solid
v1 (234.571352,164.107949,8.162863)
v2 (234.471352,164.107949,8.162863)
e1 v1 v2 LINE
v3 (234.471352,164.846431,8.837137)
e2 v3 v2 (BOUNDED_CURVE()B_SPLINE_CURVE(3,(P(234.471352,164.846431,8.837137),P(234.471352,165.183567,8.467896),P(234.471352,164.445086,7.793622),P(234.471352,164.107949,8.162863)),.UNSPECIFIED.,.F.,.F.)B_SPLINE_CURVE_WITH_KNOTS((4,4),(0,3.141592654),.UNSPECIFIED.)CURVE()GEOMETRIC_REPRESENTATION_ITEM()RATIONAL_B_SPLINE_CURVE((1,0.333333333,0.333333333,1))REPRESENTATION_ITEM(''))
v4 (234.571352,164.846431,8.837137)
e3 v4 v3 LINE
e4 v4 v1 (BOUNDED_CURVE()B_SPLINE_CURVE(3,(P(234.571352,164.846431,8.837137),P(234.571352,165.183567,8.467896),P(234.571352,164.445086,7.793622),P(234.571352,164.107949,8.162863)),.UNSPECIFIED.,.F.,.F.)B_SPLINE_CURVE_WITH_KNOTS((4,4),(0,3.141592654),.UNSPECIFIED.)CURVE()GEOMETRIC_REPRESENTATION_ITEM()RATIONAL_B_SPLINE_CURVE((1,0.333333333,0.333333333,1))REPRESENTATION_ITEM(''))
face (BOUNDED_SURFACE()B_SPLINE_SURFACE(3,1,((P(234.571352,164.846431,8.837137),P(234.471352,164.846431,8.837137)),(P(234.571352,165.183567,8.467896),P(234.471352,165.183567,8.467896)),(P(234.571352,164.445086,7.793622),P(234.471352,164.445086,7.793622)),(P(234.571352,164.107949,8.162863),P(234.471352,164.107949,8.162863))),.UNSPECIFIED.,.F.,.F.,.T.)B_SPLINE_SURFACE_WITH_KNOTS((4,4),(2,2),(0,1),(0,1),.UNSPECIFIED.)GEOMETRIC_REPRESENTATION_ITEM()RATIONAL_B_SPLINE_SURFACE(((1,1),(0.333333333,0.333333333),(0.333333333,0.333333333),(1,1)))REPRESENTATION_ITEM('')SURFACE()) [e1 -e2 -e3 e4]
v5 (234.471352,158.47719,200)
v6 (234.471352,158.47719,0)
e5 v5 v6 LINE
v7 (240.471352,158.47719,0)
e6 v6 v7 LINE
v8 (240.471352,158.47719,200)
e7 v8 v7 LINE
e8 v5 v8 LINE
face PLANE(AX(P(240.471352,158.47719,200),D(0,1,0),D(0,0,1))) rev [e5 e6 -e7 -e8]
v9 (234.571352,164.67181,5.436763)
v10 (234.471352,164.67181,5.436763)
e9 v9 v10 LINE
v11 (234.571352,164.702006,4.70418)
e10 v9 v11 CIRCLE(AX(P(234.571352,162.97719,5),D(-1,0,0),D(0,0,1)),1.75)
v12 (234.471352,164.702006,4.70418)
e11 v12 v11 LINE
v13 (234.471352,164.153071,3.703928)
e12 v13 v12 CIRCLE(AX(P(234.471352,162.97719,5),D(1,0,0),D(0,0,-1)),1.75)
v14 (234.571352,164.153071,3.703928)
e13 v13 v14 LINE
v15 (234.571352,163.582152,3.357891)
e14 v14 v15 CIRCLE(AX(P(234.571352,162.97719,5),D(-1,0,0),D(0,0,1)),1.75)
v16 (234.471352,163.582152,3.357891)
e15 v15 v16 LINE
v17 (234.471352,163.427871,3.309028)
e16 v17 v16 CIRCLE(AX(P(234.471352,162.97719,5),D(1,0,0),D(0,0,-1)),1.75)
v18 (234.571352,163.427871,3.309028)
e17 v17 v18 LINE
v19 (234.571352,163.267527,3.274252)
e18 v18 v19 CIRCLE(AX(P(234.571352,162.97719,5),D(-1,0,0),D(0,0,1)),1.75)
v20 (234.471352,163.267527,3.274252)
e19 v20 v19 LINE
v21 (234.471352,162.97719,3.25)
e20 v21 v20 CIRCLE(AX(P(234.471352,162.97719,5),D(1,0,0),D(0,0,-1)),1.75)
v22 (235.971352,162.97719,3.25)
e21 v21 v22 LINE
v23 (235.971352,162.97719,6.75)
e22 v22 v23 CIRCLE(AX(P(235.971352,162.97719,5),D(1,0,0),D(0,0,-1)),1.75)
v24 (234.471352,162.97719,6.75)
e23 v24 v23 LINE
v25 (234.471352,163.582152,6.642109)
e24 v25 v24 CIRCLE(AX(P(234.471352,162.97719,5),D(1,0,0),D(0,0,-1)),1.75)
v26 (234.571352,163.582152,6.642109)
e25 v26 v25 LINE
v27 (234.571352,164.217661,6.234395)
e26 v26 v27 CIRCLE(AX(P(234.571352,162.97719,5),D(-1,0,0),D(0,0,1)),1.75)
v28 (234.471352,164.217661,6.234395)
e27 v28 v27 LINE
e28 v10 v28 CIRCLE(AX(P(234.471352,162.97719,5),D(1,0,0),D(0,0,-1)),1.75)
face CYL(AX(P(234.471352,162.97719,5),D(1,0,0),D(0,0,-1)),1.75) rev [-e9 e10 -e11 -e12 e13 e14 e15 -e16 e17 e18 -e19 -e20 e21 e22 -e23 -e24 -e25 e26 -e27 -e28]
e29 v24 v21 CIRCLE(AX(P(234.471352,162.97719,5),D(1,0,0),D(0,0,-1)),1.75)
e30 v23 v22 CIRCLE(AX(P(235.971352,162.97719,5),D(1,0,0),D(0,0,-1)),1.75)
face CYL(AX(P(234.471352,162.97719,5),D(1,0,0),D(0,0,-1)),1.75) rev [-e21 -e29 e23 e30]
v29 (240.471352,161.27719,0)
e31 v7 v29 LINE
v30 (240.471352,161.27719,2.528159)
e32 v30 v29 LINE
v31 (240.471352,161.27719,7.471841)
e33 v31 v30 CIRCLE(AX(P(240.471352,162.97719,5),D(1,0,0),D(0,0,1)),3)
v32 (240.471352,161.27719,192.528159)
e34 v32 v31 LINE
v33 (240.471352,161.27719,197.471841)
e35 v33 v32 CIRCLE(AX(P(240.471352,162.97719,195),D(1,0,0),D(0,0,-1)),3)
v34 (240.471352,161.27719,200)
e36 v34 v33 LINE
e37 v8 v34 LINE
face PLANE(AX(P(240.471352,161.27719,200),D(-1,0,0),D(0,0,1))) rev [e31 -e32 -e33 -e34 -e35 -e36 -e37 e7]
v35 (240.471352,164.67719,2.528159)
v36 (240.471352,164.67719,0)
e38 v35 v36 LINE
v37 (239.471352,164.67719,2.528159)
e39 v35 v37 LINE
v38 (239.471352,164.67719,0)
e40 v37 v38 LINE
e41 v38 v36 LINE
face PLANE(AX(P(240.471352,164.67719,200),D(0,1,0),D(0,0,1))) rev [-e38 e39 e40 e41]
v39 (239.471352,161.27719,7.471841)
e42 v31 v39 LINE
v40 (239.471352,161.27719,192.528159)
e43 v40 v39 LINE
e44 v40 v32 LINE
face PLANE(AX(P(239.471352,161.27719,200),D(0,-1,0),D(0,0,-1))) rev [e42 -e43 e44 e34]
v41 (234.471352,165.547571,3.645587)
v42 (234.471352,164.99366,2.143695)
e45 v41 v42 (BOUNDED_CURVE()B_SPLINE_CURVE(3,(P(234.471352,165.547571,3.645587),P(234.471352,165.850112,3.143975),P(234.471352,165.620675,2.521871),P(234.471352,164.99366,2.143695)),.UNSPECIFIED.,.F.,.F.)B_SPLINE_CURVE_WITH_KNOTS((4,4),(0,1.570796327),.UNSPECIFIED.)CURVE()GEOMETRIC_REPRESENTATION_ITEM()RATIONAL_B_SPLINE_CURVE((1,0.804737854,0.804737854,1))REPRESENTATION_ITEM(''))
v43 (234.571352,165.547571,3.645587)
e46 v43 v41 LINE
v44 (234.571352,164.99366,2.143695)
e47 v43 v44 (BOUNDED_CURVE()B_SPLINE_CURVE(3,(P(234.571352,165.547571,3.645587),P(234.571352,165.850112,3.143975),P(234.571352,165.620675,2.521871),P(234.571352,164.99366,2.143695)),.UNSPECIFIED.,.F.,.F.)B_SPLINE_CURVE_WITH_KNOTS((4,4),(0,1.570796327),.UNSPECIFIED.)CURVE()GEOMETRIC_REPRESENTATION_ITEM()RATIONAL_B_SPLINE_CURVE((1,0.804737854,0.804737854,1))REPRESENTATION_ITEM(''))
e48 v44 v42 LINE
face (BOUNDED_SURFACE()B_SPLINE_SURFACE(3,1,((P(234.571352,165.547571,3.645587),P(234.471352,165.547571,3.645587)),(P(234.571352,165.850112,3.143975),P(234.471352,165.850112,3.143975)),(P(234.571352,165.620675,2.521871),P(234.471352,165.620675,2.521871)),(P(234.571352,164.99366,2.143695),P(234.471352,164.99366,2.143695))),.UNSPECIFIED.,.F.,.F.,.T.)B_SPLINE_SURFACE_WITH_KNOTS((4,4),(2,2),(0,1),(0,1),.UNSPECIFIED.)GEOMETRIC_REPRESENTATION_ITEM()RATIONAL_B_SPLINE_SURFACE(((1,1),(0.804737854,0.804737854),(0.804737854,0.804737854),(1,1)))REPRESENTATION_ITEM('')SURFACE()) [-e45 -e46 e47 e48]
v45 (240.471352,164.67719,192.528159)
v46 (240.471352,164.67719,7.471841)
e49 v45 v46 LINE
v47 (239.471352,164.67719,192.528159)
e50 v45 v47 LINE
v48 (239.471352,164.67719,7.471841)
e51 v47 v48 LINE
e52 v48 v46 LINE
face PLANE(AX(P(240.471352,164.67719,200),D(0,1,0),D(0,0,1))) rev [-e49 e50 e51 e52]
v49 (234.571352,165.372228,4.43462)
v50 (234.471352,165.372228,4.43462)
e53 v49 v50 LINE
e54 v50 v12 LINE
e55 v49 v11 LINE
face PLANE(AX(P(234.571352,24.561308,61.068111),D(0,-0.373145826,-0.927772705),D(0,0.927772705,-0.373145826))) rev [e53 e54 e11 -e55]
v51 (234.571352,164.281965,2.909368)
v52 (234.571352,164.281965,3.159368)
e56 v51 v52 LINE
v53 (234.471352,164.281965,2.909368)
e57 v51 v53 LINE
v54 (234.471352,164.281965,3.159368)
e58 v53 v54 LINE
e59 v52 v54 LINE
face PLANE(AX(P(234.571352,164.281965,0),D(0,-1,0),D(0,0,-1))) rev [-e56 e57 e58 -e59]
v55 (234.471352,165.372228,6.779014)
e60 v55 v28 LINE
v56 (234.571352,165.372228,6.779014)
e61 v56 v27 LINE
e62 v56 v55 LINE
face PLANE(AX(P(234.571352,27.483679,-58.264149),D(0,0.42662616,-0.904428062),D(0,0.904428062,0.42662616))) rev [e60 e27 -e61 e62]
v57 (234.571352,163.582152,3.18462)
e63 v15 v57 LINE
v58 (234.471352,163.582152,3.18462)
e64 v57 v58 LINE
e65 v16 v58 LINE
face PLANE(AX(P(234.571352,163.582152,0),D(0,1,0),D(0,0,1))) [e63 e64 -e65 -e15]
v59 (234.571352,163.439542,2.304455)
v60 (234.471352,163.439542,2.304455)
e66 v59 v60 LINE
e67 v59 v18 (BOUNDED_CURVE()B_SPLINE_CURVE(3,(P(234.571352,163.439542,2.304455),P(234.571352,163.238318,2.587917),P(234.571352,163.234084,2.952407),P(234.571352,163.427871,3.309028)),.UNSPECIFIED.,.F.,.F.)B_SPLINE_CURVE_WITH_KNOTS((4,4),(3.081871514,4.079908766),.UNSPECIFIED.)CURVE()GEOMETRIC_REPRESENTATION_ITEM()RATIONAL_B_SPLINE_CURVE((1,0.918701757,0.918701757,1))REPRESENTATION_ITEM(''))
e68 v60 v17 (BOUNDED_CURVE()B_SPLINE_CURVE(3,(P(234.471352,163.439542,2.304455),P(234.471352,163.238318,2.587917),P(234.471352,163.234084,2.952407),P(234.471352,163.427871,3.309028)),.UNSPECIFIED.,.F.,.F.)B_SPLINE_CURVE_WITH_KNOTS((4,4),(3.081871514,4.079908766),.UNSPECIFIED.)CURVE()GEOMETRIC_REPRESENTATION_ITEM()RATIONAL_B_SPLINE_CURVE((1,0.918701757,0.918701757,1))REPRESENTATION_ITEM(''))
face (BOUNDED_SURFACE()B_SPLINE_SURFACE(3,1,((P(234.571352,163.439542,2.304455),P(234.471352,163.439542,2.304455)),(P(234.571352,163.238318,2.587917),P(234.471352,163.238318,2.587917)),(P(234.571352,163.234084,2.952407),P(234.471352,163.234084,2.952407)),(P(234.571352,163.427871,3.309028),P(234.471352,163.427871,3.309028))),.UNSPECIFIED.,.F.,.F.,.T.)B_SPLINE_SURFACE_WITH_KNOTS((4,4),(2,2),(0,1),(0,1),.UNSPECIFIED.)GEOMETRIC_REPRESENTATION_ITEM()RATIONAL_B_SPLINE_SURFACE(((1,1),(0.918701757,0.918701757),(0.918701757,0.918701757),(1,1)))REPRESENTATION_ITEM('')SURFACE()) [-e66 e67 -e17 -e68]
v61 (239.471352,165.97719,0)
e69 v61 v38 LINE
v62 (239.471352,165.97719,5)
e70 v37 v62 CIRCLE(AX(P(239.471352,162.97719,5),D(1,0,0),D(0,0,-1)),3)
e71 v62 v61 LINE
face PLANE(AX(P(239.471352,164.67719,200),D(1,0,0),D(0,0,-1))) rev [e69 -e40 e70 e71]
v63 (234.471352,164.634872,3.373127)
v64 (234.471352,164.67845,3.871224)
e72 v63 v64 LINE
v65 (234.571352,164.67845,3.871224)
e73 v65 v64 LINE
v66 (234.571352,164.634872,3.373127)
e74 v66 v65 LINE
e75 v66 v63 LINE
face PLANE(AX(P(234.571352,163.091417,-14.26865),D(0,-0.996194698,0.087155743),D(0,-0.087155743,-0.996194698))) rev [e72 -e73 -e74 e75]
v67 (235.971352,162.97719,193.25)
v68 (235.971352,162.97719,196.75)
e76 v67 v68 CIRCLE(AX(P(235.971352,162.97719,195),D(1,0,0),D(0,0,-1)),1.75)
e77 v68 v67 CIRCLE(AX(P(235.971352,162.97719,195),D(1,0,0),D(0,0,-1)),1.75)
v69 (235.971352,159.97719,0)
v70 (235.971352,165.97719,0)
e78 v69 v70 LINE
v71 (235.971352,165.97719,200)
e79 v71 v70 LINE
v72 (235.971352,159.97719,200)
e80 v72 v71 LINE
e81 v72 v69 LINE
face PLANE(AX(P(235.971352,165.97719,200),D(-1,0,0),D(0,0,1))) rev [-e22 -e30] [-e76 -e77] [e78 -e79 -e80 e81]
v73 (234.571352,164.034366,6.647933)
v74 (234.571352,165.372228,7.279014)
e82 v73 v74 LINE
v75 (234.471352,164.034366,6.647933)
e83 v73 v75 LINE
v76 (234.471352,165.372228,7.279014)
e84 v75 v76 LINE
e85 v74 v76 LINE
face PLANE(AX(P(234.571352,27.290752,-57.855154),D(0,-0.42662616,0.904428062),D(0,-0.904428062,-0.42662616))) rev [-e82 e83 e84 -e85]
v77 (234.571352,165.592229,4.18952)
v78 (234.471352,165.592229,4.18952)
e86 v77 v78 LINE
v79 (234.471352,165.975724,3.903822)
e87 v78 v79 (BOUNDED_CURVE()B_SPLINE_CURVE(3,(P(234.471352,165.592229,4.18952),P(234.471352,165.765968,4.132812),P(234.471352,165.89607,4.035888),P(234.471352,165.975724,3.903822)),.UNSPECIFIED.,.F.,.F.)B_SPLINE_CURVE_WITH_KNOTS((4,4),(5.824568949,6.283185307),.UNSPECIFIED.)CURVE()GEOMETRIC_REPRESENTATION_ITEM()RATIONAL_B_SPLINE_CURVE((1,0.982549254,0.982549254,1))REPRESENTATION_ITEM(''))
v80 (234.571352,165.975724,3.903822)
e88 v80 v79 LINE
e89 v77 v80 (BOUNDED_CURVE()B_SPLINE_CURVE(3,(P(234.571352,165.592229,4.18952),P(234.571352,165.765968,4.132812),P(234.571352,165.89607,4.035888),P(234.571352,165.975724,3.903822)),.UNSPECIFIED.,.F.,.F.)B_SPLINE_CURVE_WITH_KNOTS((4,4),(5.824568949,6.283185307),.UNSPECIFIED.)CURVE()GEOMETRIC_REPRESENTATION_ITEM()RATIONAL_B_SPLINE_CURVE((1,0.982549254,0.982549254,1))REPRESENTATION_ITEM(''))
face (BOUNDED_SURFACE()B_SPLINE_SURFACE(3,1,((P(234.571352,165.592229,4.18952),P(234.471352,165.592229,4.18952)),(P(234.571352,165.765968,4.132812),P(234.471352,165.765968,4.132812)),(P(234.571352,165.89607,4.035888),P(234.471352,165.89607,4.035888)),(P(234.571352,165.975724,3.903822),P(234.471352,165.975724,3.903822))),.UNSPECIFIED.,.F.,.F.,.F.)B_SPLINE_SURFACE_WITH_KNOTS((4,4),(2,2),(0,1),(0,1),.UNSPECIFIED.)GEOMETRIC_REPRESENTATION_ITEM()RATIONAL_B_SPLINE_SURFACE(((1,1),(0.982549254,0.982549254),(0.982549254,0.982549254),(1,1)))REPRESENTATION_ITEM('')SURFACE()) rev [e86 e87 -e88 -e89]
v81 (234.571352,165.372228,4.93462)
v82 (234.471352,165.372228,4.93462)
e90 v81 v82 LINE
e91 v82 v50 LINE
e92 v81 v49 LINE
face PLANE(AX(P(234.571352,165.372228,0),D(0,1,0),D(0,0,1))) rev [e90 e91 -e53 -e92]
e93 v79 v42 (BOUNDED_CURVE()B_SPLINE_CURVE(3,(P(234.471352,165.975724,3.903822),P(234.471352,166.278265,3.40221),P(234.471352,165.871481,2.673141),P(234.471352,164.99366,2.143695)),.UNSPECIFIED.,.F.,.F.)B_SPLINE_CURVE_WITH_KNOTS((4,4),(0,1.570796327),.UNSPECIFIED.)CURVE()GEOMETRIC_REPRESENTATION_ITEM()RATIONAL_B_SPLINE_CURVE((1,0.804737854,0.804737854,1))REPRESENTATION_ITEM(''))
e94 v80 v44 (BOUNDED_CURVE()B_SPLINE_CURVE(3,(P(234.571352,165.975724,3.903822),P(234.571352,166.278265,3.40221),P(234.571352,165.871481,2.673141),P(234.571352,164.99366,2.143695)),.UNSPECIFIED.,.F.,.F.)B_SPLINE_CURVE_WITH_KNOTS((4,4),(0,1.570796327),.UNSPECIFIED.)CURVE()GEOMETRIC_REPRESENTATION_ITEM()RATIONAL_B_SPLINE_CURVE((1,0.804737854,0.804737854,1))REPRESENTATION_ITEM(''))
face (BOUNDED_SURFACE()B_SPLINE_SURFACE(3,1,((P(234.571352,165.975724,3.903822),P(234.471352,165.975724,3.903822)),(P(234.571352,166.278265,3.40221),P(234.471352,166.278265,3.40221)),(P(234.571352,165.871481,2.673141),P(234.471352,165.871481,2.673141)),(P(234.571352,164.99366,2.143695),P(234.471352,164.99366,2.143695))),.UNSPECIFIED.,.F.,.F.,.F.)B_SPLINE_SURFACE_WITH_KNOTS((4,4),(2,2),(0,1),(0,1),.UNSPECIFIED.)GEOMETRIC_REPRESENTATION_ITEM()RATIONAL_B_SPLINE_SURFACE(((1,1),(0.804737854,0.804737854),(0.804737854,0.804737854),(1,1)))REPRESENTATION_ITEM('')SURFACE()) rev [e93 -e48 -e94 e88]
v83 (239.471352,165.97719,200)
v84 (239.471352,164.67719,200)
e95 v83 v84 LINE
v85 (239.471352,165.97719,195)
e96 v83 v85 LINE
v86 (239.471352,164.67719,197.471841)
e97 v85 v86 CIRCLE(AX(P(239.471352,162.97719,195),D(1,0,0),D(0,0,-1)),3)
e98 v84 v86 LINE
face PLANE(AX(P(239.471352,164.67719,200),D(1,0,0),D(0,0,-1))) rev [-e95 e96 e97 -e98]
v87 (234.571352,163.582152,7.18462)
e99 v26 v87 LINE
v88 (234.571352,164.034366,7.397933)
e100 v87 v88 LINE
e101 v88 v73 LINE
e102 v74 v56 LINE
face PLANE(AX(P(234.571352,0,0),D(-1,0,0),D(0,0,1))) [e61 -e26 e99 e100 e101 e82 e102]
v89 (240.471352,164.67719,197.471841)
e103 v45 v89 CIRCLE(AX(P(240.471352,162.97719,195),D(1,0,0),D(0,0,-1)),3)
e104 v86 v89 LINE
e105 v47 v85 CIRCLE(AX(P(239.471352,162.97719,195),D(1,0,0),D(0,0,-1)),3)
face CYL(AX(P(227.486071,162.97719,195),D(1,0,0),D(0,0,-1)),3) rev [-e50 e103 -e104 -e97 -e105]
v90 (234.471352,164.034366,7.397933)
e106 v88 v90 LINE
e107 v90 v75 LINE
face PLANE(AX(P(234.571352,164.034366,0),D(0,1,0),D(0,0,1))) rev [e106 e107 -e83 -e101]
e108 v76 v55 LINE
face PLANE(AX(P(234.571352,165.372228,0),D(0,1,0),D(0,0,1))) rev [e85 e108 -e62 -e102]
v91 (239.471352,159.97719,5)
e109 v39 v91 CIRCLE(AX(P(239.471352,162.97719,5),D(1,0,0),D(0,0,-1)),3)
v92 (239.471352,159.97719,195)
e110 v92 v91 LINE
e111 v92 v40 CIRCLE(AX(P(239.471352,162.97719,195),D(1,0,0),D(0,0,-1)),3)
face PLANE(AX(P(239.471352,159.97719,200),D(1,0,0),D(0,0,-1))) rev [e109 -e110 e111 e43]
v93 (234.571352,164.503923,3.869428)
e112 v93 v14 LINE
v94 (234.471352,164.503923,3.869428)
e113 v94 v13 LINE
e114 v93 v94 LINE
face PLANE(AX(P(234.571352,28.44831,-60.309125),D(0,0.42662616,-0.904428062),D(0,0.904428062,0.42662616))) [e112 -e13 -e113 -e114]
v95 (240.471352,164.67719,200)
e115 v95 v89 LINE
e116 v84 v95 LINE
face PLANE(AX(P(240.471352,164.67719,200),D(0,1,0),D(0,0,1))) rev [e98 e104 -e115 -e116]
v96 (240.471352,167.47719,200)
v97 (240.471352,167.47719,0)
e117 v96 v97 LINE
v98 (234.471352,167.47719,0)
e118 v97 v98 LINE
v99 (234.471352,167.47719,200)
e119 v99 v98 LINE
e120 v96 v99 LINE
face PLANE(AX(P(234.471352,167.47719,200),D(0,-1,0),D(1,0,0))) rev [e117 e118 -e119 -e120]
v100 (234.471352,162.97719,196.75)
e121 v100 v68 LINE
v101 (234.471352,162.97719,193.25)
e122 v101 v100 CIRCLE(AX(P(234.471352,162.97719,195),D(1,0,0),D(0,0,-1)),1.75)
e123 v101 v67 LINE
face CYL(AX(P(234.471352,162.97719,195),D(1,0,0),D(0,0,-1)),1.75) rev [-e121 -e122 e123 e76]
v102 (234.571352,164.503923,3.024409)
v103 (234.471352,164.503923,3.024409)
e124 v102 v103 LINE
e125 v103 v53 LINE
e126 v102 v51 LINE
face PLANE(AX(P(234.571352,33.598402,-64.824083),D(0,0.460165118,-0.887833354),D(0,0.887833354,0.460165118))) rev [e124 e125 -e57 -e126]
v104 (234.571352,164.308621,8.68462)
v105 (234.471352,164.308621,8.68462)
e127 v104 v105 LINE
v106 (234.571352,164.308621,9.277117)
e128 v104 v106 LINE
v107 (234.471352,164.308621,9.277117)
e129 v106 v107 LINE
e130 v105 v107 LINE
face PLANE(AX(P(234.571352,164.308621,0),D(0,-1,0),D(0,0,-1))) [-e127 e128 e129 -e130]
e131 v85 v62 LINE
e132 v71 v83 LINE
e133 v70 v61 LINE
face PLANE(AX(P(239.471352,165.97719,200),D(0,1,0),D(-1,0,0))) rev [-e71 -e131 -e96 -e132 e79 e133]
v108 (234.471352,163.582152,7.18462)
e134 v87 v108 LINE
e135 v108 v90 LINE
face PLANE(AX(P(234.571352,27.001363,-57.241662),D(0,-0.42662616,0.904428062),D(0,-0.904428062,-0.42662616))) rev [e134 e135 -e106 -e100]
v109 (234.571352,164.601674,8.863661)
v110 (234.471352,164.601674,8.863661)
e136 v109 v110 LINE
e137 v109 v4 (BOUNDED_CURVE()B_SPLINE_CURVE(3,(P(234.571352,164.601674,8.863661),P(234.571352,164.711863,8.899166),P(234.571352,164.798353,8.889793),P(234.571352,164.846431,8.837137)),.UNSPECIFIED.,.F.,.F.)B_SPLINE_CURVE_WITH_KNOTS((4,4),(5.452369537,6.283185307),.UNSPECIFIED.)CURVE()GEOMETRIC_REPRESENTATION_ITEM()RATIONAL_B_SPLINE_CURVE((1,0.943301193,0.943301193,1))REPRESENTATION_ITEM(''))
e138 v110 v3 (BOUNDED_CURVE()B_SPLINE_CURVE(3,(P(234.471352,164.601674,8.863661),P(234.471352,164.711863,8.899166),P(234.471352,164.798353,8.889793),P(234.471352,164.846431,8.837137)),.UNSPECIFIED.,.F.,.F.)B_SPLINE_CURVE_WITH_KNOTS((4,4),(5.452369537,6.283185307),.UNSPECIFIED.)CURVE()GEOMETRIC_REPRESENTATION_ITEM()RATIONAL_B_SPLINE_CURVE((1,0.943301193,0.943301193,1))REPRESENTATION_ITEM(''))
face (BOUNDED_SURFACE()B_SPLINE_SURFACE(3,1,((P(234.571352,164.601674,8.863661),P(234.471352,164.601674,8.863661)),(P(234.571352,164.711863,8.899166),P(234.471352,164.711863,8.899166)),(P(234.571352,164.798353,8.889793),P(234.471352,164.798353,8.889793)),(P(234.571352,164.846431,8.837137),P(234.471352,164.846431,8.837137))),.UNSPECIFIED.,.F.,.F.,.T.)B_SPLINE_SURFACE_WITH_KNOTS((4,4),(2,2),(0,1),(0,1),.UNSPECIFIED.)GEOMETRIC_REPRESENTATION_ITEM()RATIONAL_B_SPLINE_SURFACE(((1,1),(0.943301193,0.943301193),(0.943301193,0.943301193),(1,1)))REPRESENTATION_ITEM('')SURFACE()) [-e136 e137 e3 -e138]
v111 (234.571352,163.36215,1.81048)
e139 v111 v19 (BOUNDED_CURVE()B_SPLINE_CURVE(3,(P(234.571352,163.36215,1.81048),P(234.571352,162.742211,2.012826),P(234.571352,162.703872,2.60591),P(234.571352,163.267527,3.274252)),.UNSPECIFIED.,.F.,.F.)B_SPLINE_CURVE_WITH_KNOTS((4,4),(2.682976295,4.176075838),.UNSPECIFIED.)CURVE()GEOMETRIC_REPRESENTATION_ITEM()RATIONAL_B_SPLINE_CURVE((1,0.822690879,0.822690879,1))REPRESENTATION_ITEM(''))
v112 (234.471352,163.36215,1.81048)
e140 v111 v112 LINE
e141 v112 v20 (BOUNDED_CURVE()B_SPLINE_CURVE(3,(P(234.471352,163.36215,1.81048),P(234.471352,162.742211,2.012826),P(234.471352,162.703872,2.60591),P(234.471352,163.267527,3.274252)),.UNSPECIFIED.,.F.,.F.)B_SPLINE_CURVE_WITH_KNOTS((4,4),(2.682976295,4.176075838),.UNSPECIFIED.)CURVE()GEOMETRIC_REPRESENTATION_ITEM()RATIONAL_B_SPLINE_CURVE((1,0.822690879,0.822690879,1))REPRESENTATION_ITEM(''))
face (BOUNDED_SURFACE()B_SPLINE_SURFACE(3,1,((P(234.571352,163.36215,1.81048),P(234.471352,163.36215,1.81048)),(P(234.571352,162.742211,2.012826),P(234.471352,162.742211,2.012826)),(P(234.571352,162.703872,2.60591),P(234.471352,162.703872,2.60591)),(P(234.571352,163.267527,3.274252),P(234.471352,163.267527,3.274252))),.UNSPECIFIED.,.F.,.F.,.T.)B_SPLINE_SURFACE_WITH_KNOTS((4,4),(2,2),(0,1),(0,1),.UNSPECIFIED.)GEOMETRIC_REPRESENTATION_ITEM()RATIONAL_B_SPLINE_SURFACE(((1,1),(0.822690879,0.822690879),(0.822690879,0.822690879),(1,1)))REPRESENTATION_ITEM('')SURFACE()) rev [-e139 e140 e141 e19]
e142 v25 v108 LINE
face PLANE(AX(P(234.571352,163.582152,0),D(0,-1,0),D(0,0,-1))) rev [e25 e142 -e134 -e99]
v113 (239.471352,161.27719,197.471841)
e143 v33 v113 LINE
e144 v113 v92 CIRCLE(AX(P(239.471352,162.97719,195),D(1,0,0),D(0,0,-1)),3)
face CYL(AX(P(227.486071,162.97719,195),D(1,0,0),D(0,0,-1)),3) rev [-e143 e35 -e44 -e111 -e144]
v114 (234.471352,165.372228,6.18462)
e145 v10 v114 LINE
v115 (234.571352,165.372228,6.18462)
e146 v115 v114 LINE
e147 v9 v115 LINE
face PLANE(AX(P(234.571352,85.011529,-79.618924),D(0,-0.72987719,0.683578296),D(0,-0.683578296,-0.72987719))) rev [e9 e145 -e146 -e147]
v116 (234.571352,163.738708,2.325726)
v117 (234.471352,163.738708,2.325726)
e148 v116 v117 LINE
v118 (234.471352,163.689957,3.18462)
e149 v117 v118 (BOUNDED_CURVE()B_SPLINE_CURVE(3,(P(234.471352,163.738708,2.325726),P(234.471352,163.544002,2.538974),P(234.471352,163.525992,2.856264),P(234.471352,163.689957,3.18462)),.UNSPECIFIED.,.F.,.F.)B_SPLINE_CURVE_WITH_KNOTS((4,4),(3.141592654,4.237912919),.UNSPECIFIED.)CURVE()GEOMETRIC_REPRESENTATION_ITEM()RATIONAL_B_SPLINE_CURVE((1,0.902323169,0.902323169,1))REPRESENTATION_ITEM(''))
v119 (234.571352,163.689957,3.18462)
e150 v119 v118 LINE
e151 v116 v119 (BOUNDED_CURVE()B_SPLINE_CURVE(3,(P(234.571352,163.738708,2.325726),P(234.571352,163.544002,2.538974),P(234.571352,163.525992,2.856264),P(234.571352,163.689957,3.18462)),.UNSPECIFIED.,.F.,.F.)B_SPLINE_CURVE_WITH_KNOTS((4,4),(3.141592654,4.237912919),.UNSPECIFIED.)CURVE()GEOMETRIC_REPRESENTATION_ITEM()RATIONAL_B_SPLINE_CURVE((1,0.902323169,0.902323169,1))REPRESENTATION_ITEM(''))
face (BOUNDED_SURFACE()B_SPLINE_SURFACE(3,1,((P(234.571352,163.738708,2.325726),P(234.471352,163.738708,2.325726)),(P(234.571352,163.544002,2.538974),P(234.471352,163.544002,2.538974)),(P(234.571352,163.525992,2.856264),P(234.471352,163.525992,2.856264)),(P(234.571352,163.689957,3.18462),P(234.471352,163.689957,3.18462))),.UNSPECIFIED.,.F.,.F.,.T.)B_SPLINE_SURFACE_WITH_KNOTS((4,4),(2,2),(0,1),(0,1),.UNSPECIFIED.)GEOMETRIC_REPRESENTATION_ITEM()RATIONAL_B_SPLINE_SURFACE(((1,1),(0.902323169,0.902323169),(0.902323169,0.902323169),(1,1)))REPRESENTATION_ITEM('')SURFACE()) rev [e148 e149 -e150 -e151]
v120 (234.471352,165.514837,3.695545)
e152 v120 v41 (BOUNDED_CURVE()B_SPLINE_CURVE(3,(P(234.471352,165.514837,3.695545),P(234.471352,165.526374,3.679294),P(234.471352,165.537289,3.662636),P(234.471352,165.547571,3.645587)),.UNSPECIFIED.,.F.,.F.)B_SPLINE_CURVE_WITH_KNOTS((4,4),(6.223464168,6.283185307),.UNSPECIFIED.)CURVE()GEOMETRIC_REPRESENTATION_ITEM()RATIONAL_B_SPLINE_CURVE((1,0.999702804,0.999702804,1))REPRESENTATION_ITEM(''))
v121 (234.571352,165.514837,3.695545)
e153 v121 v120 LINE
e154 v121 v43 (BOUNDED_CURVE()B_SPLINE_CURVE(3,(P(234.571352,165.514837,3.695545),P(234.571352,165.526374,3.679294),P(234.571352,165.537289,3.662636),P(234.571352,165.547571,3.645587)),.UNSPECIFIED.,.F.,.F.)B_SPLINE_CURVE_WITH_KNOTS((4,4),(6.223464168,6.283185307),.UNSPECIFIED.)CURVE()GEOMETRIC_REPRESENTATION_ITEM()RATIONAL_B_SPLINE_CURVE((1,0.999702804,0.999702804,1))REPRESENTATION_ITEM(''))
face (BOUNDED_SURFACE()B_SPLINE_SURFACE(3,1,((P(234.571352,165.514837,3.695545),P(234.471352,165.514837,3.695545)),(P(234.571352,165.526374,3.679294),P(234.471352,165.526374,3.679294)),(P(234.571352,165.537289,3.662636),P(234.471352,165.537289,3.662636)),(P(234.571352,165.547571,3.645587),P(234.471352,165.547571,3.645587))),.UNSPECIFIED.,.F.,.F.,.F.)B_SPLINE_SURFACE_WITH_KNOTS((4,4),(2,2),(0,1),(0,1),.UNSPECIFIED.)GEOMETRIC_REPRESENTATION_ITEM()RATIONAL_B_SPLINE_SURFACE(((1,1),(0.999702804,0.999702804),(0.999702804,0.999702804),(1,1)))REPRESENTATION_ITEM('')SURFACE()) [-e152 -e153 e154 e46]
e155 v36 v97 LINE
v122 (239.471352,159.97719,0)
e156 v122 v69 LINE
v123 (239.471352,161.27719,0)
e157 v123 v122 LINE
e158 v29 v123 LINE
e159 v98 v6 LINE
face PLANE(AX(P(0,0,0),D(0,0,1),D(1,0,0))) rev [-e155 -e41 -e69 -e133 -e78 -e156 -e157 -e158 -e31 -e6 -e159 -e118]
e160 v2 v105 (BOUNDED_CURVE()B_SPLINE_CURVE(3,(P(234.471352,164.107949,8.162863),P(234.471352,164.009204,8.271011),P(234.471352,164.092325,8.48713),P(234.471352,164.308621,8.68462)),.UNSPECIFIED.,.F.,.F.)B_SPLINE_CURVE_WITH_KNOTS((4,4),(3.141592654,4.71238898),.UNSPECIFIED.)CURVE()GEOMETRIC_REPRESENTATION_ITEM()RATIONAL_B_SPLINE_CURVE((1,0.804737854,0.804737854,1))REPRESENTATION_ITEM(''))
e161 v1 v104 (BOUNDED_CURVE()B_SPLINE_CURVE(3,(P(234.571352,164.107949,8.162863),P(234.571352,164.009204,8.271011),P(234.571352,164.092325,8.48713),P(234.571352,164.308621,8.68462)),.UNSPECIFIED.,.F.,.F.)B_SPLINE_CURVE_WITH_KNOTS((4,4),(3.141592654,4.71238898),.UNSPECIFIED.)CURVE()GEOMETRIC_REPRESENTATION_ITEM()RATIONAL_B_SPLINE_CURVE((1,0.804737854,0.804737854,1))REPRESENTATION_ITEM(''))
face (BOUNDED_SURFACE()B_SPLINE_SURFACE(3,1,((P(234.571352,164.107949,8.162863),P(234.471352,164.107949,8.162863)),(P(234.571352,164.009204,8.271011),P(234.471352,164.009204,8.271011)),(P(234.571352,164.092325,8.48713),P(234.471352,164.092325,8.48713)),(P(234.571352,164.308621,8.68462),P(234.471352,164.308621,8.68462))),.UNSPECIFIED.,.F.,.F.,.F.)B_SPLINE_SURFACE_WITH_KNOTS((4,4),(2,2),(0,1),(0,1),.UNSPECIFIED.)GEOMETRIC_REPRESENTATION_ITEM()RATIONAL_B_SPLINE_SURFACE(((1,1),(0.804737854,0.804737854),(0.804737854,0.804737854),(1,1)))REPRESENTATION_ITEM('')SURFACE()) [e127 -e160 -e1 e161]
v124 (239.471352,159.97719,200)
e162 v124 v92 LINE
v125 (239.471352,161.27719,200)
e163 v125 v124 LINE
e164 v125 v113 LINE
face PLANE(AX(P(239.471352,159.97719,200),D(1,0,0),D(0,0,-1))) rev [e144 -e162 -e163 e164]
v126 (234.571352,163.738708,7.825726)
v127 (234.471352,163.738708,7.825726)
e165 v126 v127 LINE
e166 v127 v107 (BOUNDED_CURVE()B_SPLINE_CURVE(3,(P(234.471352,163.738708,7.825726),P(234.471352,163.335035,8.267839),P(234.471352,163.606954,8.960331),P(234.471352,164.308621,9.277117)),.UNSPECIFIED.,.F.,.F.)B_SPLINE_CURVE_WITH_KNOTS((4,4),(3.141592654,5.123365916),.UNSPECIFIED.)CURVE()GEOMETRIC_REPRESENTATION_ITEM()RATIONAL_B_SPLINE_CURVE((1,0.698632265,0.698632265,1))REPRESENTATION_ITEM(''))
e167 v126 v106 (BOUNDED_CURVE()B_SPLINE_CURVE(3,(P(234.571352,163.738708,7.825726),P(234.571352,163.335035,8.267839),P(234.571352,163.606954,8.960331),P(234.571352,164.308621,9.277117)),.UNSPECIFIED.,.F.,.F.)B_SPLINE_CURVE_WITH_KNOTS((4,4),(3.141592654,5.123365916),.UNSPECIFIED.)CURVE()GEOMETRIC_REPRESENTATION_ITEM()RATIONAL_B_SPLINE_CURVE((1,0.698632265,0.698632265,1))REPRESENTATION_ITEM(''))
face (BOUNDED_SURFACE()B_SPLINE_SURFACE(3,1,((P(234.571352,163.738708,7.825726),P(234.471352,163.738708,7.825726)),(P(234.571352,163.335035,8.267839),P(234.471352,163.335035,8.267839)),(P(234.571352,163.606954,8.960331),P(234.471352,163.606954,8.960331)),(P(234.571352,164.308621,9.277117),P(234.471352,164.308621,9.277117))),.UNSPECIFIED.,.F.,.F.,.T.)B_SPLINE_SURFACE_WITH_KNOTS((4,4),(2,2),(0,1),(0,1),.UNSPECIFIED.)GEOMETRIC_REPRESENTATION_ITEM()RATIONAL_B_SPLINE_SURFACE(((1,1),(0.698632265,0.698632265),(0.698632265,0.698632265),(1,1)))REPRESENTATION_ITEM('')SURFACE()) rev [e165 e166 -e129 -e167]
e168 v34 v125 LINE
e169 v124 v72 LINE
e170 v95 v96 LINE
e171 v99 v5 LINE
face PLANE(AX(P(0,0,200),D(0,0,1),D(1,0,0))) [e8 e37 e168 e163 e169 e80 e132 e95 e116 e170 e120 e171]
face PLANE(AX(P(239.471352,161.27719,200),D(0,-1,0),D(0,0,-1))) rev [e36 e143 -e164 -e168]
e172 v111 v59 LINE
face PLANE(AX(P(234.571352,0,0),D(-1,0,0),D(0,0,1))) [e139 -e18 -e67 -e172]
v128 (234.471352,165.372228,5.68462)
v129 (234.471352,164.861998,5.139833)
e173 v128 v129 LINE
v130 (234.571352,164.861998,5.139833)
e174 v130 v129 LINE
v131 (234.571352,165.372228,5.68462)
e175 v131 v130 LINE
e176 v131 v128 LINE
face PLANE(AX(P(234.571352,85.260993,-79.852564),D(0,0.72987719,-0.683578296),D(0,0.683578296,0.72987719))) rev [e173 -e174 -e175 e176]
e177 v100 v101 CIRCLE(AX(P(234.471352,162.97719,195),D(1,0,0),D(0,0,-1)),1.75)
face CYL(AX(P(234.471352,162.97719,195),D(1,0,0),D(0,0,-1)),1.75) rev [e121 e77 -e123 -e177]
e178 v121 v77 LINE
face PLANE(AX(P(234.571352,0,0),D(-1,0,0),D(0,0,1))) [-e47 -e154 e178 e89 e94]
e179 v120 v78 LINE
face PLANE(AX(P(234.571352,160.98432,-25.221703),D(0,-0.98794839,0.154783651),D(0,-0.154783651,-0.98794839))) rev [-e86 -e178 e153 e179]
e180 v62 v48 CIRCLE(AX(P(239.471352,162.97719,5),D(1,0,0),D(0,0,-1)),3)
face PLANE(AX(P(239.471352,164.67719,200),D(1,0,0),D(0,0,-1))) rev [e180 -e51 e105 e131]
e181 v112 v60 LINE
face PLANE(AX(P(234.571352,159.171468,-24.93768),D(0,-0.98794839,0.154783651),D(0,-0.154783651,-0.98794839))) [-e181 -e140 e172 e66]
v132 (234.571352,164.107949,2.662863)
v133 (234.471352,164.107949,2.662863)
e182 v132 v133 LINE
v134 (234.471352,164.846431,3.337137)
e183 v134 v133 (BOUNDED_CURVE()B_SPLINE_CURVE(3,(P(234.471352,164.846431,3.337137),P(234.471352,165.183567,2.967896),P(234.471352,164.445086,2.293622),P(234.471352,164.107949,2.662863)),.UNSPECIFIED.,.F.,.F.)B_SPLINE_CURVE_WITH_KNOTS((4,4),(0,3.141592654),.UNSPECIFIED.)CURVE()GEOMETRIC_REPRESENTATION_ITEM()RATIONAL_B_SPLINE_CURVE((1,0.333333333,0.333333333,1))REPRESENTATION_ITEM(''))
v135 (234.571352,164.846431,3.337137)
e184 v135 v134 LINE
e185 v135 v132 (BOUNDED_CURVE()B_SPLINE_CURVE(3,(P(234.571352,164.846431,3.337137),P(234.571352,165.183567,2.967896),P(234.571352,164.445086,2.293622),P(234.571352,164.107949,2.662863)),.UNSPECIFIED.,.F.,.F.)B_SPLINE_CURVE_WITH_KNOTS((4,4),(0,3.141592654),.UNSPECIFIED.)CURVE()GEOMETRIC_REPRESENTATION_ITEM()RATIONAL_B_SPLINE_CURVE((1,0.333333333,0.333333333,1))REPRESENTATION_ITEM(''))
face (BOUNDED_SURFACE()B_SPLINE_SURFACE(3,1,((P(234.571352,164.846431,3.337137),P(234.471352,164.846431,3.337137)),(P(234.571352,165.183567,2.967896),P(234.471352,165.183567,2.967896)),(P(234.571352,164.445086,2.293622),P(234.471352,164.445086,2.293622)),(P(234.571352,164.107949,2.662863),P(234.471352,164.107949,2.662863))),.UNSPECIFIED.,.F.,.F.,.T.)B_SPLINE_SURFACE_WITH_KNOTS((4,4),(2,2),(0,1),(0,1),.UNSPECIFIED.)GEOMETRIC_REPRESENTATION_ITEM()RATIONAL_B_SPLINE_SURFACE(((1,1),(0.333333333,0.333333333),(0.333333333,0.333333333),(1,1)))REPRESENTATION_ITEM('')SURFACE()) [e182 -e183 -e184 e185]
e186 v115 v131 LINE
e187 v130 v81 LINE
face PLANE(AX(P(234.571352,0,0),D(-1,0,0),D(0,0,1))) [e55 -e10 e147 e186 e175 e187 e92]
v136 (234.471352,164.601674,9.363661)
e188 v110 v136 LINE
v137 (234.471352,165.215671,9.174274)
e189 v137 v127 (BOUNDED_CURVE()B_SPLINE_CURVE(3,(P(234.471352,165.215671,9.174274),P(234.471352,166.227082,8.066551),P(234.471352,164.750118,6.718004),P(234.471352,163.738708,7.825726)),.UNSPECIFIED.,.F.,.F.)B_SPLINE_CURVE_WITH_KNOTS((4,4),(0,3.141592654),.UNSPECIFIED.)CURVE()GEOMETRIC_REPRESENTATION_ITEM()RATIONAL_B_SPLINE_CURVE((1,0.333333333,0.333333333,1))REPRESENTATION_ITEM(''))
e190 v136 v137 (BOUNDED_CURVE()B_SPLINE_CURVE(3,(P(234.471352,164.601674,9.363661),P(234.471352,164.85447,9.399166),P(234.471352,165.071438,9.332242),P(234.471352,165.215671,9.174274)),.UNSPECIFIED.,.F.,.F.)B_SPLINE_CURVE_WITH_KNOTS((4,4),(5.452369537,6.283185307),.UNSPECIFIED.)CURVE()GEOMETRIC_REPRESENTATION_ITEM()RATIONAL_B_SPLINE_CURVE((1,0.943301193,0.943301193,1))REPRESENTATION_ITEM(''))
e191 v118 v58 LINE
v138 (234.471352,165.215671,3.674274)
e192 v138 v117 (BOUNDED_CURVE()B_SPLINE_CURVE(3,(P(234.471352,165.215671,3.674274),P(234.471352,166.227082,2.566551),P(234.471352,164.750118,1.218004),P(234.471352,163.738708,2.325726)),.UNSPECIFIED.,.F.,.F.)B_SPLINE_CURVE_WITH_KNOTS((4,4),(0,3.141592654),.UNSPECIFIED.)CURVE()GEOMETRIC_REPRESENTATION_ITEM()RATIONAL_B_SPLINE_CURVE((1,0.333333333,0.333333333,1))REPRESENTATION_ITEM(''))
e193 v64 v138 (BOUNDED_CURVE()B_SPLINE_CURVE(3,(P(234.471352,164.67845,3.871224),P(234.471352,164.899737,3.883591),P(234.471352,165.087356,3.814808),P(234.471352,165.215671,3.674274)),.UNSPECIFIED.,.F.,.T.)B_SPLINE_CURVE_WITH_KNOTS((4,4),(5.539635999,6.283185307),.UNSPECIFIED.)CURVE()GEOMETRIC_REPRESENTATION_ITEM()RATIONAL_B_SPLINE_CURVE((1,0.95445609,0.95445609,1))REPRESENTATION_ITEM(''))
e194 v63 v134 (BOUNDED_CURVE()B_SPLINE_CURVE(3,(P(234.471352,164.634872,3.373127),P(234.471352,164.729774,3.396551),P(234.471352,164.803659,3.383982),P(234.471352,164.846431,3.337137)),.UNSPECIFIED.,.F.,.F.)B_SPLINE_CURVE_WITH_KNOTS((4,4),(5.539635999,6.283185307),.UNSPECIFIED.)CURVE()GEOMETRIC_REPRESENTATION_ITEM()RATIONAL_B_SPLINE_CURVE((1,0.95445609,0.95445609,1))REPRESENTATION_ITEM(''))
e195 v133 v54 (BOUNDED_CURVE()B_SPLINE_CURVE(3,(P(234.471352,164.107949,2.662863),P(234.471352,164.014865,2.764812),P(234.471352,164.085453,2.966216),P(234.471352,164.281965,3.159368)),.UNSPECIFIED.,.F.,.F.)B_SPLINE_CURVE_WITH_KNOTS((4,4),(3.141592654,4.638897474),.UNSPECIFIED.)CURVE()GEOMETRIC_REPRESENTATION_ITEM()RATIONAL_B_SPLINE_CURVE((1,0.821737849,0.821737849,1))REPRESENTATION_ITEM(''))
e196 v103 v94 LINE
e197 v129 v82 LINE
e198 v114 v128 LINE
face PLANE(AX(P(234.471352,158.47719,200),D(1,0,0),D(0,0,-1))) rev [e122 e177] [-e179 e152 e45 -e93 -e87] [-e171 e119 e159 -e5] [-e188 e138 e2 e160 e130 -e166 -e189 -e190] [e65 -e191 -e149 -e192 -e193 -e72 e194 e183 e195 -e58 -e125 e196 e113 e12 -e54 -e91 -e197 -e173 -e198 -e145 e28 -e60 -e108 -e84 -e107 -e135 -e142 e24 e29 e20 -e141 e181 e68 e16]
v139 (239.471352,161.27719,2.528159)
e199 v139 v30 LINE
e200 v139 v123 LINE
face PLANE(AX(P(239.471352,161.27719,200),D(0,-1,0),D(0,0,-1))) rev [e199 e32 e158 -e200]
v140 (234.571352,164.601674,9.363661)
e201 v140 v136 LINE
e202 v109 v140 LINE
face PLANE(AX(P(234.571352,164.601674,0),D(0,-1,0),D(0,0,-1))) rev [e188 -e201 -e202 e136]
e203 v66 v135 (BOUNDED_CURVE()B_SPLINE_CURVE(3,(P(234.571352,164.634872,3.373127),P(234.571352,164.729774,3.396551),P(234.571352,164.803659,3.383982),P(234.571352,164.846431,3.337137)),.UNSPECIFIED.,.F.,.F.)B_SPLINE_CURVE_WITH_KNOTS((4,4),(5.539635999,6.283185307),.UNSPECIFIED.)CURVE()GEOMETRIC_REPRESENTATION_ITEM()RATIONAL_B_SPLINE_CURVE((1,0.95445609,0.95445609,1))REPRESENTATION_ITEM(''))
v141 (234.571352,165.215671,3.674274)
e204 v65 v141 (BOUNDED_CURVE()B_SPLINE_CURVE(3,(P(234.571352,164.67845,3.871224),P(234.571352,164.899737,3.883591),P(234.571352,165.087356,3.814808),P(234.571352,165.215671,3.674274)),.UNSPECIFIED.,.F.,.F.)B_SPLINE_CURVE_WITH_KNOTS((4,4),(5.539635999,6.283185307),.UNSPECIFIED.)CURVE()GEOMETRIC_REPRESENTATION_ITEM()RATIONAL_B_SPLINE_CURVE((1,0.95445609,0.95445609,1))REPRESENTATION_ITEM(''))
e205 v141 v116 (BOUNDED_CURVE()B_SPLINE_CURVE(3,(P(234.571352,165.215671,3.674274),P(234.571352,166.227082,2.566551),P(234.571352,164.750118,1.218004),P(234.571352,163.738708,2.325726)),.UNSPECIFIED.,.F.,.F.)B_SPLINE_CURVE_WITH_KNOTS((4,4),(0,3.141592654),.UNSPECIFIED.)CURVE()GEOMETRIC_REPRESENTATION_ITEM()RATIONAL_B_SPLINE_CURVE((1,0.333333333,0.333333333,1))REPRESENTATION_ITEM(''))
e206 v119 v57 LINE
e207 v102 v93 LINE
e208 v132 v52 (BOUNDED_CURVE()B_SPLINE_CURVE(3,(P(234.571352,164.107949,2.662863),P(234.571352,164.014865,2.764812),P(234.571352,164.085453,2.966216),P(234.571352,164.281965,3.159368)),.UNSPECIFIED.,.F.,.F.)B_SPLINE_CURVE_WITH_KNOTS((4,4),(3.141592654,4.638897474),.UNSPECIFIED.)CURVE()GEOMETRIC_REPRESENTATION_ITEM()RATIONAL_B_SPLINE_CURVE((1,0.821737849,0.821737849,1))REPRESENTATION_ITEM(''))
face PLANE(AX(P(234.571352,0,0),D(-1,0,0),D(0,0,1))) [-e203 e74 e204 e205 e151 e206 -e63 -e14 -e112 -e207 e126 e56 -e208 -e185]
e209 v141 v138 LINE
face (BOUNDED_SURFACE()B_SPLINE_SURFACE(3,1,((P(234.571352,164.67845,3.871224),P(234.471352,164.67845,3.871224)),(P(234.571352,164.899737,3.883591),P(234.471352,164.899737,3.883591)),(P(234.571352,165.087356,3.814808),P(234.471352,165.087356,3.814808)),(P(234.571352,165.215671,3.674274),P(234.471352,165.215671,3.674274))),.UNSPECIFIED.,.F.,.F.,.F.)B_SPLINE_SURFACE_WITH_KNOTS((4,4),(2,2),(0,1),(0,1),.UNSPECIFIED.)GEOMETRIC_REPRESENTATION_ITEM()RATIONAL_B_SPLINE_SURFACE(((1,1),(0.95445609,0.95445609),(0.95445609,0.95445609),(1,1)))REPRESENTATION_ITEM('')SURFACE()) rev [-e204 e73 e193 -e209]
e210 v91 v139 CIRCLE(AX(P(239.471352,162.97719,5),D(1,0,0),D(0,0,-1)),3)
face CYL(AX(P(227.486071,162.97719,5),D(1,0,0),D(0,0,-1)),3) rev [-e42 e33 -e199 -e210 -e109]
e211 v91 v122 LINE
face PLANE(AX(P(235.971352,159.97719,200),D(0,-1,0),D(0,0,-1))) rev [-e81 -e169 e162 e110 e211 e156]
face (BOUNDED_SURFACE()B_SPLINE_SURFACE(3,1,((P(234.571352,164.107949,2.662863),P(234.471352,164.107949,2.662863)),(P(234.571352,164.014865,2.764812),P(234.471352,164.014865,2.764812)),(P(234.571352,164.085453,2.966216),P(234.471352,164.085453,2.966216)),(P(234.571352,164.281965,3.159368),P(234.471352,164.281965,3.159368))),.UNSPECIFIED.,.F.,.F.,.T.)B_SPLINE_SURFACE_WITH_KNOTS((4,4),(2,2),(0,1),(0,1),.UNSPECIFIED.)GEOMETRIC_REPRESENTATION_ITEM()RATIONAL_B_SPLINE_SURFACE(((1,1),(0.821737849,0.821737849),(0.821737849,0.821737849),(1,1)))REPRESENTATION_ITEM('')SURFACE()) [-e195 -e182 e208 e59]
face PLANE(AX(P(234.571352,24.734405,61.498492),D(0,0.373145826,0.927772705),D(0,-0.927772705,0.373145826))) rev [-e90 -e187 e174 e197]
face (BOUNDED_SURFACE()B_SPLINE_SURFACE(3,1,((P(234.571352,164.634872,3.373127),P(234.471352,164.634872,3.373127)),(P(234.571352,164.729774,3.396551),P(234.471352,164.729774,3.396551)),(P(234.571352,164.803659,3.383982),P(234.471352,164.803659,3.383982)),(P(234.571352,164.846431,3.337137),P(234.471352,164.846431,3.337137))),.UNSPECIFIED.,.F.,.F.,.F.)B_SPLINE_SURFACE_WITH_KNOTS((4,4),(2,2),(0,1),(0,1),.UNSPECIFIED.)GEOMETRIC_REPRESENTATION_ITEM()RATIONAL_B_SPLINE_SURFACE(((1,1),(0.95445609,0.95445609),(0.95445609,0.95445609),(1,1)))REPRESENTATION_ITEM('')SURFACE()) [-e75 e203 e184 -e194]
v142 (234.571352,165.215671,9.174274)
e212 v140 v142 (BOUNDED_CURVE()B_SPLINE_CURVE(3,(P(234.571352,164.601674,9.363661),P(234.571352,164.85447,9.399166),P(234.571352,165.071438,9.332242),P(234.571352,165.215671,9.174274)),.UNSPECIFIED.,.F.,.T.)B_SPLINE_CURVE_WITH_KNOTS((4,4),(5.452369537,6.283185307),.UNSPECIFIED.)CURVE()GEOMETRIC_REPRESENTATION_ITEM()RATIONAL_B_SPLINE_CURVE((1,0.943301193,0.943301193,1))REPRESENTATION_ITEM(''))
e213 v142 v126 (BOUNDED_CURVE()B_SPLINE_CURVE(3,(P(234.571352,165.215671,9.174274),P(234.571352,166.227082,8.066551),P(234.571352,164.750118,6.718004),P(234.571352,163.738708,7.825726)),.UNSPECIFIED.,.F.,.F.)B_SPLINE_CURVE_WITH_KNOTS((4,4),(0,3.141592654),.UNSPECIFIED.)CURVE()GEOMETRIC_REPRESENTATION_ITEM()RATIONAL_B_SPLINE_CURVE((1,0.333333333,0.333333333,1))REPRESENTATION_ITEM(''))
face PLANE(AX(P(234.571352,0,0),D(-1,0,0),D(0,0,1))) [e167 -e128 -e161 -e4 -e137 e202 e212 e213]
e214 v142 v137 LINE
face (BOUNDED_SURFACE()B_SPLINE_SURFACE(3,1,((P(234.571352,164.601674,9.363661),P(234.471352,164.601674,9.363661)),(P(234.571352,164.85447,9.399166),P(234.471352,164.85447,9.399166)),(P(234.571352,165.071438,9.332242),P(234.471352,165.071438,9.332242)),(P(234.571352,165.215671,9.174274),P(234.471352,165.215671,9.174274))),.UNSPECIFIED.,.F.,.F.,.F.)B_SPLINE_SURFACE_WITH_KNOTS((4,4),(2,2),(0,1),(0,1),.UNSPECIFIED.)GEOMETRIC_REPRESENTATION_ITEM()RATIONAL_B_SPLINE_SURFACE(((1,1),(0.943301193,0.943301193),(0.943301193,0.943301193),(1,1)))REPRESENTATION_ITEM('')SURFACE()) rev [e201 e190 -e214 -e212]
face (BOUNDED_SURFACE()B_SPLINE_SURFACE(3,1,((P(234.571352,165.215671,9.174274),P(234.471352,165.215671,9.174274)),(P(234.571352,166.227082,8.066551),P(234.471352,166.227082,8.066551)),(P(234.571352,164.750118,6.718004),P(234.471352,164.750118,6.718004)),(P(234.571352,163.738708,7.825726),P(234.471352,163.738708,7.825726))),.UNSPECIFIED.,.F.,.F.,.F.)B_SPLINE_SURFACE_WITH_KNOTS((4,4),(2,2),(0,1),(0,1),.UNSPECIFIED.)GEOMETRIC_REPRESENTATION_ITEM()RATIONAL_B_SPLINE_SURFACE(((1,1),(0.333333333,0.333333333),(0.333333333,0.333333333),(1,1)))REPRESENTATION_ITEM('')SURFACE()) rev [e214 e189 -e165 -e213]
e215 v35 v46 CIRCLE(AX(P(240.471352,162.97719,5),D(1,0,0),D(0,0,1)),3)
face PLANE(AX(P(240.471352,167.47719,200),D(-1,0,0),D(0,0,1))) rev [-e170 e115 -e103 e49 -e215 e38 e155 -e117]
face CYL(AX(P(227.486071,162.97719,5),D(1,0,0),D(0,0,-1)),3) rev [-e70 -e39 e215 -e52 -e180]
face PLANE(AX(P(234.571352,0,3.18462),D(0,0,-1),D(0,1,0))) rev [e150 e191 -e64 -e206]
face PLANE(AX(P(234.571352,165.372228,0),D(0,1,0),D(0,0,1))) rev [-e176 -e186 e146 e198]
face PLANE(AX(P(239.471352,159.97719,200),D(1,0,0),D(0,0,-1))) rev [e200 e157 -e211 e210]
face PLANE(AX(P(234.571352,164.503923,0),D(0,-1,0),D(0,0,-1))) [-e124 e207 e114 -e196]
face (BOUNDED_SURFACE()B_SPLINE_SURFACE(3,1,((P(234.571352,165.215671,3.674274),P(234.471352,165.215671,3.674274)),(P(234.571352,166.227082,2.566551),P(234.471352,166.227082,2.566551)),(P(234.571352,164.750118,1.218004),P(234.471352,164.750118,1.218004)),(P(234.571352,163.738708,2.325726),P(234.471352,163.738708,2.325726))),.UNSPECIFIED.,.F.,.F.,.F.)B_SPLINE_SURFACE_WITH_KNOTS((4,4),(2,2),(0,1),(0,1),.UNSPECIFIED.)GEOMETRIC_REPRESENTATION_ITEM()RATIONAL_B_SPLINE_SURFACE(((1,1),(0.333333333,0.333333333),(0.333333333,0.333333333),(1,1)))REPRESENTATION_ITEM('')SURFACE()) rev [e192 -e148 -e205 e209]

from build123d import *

# Parameters (mm, degrees)
EXTRUDE_1_DEPTH     = 200
CUT_EXTRUDE_1_DEPTH = 0.1
SKETCH_3_R          = 3
CUT_EXTRUDE_2_DEPTH = 4.5
SKETCH_4_R          = 1.75
CUT_EXTRUDE_3_DEPTH = 261.9000942


with BuildPart() as part:
    # Model → 凸台-拉伸1 (new body)
    with BuildSketch(Plane.XY):
        Polygon((235.971352115, 159.97718973), (239.471352115, 159.97718973), (239.471352115, 161.27718973), (240.471352115, 161.27718973), (240.471352115, 158.47718973), (234.471352115, 158.47718973), (234.471352115, 167.47718973), (240.471352115, 167.47718973), (240.471352115, 164.67718973), (239.471352115, 164.67718973), (239.471352115, 165.97718973), (235.971352115, 165.97718973), align=None)
    extrude(amount=EXTRUDE_1_DEPTH)

    # 草图2 → 切除-拉伸1 (cut)
    with BuildSketch(Plane(origin=(234.471352115, 157.934205003, -3.551128869), x_dir=(0, 0, 1), z_dir=(-1, 0, 0))):
        with BuildLine():
            Line((12.414790076, 6.667469393), (12.914790076, 6.667469393))
            add(Edge.make_bspline(
                [(12.914790076, 6.667469393), (13.105445322, 8.024946973), (11.817726071, 7.304400271), (10.53000682, 6.583853569), (11.375222173, 5.806000114), (12.220437527, 5.02814666), (12.828246359, 6.37441634)],
                knots=[2.310776883, 2.310776883, 2.310776883, 4.295504112, 4.295504112, 6.280231341, 6.280231341, 8.26495857, 8.26495857, 8.26495857], degree=2, weights=[1, 0.546712287, 1, 0.546712287, 1, 0.546712287, 1]))
            Line((12.828246359, 6.37441634), (12.235749287, 6.37441634))
            add(Edge.make_bspline(
                [(12.414790076, 6.667469393), (12.579589729, 7.17892596), (12.071440891, 6.880567221), (11.563292052, 6.582208482), (11.676360556, 6.233901737), (11.789429059, 5.885594992), (12.235749287, 6.37441634)],
                knots=[2.310776883, 2.310776883, 2.310776883, 4.1585118, 4.1585118, 6.006246717, 6.006246717, 7.853981634, 7.853981634, 7.853981634], degree=2, weights=[1, 0.602738677, 1, 0.602738677, 1, 0.602738677, 1]))
        make_face()
        Polygon((10.199062367, 6.100160833), (10.830142798, 7.438022654), (10.330142798, 7.438022654), (9.485749287, 5.647946802), (10.735749287, 5.647946802), (10.949062367, 6.100160833), align=None)
        Polygon((8.82776943, 6.587639422), (8.485749287, 5.647946802), (7.985749287, 5.647946802), (8.32776943, 6.587639422), (7.985749287, 7.438022654), (8.485749287, 7.438022654), (8.690961373, 6.927792715), (9.235749287, 7.438022654), (9.735749287, 7.438022654), align=None)
        with BuildLine():
            add(Edge.make_bspline(
                [(7.246674356, 7.580632375), (6.380164872, 8.195748474), (5.694823482, 7.059454556)],
                knots=[6.223464168, 6.223464168, 6.223464168, 7.853981634, 7.853981634, 7.853981634], degree=2, weights=[1, 0.685680084, 1]))
            add(Edge.make_bspline(
                [(7.740648551, 7.658024201), (7.149045607, 9.470550368), (5.694823482, 7.059454556)],
                knots=[5.824568949, 5.824568949, 5.824568949, 7.853981634, 7.853981634, 7.853981634], degree=2, weights=[1, 0.527869365, 1]))
            Line((7.740648551, 7.658024201), (7.246674356, 7.580632375))
        make_face()
        with BuildLine():
            Line((6.924255788, 6.700667335), (7.422353137, 6.744245207))
            add(Edge.make_bspline(
                [(7.422353137, 6.744245207), (7.566792843, 9.328849149), (5.887544801, 6.911260491), (4.208296758, 4.493671833), (6.735749287, 5.755751762)],
                knots=[5.539635999, 5.539635999, 5.539635999, 8.030367113, 8.030367113, 10.521098226, 10.521098226, 10.521098226], degree=2, weights=[1, 0.319716976, 1, 0.319716976, 1]))
            Line((6.735749287, 5.755751762), (6.735749287, 5.647946802))
            Line((6.735749287, 5.647946802), (6.985749287, 5.647946802))
            Line((6.985749287, 5.647946802), (7.42055637, 6.569718047))
            Line((7.42055637, 6.569718047), (6.575537831, 6.569718047))
            Line((6.575537831, 6.569718047), (6.460496551, 6.347759709))
            Line((6.460496551, 6.347759709), (6.710496551, 6.347759709))
            add(Edge.make_bspline(
                [(6.924255788, 6.700667335), (7.039891919, 7.169169172), (6.558503894, 6.872786595), (6.07711587, 6.576404017), (6.174734812, 6.239199772), (6.272353754, 5.901995526), (6.710496551, 6.347759709)],
                knots=[5.539635999, 5.539635999, 5.539635999, 7.333784926, 7.333784926, 9.127933854, 9.127933854, 10.922082781, 10.922082781, 10.922082781], degree=2, weights=[1, 0.623898956, 1, 0.623898956, 1, 0.623898956, 1]))
        make_face()
        with BuildLine():
            add(Edge.make_bspline(
                [(5.855583383, 5.505337081), (6.722092867, 4.890220982), (7.407434257, 6.0265149)],
                knots=[3.081871514, 3.081871514, 3.081871514, 4.71238898, 4.71238898, 4.71238898], degree=2, weights=[1, 0.685680084, 1]))
            add(Edge.make_bspline(
                [(5.361609188, 5.427945255), (5.953212132, 3.615419087), (7.407434257, 6.0265149)],
                knots=[2.682976295, 2.682976295, 2.682976295, 4.71238898, 4.71238898, 4.71238898], degree=2, weights=[1, 0.527869365, 1]))
            Line((5.361609188, 5.427945255), (5.855583383, 5.505337081))
        make_face()
    extrude(amount=-CUT_EXTRUDE_1_DEPTH, mode=Mode.SUBTRACT)

    # 草图3 → 切除-拉伸2 (cut)
    with BuildSketch(Plane(origin=(240.471352115, 0, 0), x_dir=(0, 0, -1), z_dir=(1, 0, 0))):
        with Locations((-195, 162.97718973)):
            Circle(SKETCH_3_R)
        with Locations((-5, 162.97718973)):
            Circle(SKETCH_3_R)
    extrude(amount=-CUT_EXTRUDE_2_DEPTH, mode=Mode.SUBTRACT)

    # 草图4 → 切除-拉伸3 (cut, through all)
    with BuildSketch(Plane(origin=(235.971352115, 0, 0), x_dir=(0, 0, -1), z_dir=(1, 0, 0))):
        with Locations((-195, 162.97718973)):
            Circle(SKETCH_4_R)
        with Locations((-5, 162.97718973)):
            Circle(SKETCH_4_R)
    extrude(amount=-CUT_EXTRUDE_3_DEPTH, mode=Mode.SUBTRACT)


solid = part.part
